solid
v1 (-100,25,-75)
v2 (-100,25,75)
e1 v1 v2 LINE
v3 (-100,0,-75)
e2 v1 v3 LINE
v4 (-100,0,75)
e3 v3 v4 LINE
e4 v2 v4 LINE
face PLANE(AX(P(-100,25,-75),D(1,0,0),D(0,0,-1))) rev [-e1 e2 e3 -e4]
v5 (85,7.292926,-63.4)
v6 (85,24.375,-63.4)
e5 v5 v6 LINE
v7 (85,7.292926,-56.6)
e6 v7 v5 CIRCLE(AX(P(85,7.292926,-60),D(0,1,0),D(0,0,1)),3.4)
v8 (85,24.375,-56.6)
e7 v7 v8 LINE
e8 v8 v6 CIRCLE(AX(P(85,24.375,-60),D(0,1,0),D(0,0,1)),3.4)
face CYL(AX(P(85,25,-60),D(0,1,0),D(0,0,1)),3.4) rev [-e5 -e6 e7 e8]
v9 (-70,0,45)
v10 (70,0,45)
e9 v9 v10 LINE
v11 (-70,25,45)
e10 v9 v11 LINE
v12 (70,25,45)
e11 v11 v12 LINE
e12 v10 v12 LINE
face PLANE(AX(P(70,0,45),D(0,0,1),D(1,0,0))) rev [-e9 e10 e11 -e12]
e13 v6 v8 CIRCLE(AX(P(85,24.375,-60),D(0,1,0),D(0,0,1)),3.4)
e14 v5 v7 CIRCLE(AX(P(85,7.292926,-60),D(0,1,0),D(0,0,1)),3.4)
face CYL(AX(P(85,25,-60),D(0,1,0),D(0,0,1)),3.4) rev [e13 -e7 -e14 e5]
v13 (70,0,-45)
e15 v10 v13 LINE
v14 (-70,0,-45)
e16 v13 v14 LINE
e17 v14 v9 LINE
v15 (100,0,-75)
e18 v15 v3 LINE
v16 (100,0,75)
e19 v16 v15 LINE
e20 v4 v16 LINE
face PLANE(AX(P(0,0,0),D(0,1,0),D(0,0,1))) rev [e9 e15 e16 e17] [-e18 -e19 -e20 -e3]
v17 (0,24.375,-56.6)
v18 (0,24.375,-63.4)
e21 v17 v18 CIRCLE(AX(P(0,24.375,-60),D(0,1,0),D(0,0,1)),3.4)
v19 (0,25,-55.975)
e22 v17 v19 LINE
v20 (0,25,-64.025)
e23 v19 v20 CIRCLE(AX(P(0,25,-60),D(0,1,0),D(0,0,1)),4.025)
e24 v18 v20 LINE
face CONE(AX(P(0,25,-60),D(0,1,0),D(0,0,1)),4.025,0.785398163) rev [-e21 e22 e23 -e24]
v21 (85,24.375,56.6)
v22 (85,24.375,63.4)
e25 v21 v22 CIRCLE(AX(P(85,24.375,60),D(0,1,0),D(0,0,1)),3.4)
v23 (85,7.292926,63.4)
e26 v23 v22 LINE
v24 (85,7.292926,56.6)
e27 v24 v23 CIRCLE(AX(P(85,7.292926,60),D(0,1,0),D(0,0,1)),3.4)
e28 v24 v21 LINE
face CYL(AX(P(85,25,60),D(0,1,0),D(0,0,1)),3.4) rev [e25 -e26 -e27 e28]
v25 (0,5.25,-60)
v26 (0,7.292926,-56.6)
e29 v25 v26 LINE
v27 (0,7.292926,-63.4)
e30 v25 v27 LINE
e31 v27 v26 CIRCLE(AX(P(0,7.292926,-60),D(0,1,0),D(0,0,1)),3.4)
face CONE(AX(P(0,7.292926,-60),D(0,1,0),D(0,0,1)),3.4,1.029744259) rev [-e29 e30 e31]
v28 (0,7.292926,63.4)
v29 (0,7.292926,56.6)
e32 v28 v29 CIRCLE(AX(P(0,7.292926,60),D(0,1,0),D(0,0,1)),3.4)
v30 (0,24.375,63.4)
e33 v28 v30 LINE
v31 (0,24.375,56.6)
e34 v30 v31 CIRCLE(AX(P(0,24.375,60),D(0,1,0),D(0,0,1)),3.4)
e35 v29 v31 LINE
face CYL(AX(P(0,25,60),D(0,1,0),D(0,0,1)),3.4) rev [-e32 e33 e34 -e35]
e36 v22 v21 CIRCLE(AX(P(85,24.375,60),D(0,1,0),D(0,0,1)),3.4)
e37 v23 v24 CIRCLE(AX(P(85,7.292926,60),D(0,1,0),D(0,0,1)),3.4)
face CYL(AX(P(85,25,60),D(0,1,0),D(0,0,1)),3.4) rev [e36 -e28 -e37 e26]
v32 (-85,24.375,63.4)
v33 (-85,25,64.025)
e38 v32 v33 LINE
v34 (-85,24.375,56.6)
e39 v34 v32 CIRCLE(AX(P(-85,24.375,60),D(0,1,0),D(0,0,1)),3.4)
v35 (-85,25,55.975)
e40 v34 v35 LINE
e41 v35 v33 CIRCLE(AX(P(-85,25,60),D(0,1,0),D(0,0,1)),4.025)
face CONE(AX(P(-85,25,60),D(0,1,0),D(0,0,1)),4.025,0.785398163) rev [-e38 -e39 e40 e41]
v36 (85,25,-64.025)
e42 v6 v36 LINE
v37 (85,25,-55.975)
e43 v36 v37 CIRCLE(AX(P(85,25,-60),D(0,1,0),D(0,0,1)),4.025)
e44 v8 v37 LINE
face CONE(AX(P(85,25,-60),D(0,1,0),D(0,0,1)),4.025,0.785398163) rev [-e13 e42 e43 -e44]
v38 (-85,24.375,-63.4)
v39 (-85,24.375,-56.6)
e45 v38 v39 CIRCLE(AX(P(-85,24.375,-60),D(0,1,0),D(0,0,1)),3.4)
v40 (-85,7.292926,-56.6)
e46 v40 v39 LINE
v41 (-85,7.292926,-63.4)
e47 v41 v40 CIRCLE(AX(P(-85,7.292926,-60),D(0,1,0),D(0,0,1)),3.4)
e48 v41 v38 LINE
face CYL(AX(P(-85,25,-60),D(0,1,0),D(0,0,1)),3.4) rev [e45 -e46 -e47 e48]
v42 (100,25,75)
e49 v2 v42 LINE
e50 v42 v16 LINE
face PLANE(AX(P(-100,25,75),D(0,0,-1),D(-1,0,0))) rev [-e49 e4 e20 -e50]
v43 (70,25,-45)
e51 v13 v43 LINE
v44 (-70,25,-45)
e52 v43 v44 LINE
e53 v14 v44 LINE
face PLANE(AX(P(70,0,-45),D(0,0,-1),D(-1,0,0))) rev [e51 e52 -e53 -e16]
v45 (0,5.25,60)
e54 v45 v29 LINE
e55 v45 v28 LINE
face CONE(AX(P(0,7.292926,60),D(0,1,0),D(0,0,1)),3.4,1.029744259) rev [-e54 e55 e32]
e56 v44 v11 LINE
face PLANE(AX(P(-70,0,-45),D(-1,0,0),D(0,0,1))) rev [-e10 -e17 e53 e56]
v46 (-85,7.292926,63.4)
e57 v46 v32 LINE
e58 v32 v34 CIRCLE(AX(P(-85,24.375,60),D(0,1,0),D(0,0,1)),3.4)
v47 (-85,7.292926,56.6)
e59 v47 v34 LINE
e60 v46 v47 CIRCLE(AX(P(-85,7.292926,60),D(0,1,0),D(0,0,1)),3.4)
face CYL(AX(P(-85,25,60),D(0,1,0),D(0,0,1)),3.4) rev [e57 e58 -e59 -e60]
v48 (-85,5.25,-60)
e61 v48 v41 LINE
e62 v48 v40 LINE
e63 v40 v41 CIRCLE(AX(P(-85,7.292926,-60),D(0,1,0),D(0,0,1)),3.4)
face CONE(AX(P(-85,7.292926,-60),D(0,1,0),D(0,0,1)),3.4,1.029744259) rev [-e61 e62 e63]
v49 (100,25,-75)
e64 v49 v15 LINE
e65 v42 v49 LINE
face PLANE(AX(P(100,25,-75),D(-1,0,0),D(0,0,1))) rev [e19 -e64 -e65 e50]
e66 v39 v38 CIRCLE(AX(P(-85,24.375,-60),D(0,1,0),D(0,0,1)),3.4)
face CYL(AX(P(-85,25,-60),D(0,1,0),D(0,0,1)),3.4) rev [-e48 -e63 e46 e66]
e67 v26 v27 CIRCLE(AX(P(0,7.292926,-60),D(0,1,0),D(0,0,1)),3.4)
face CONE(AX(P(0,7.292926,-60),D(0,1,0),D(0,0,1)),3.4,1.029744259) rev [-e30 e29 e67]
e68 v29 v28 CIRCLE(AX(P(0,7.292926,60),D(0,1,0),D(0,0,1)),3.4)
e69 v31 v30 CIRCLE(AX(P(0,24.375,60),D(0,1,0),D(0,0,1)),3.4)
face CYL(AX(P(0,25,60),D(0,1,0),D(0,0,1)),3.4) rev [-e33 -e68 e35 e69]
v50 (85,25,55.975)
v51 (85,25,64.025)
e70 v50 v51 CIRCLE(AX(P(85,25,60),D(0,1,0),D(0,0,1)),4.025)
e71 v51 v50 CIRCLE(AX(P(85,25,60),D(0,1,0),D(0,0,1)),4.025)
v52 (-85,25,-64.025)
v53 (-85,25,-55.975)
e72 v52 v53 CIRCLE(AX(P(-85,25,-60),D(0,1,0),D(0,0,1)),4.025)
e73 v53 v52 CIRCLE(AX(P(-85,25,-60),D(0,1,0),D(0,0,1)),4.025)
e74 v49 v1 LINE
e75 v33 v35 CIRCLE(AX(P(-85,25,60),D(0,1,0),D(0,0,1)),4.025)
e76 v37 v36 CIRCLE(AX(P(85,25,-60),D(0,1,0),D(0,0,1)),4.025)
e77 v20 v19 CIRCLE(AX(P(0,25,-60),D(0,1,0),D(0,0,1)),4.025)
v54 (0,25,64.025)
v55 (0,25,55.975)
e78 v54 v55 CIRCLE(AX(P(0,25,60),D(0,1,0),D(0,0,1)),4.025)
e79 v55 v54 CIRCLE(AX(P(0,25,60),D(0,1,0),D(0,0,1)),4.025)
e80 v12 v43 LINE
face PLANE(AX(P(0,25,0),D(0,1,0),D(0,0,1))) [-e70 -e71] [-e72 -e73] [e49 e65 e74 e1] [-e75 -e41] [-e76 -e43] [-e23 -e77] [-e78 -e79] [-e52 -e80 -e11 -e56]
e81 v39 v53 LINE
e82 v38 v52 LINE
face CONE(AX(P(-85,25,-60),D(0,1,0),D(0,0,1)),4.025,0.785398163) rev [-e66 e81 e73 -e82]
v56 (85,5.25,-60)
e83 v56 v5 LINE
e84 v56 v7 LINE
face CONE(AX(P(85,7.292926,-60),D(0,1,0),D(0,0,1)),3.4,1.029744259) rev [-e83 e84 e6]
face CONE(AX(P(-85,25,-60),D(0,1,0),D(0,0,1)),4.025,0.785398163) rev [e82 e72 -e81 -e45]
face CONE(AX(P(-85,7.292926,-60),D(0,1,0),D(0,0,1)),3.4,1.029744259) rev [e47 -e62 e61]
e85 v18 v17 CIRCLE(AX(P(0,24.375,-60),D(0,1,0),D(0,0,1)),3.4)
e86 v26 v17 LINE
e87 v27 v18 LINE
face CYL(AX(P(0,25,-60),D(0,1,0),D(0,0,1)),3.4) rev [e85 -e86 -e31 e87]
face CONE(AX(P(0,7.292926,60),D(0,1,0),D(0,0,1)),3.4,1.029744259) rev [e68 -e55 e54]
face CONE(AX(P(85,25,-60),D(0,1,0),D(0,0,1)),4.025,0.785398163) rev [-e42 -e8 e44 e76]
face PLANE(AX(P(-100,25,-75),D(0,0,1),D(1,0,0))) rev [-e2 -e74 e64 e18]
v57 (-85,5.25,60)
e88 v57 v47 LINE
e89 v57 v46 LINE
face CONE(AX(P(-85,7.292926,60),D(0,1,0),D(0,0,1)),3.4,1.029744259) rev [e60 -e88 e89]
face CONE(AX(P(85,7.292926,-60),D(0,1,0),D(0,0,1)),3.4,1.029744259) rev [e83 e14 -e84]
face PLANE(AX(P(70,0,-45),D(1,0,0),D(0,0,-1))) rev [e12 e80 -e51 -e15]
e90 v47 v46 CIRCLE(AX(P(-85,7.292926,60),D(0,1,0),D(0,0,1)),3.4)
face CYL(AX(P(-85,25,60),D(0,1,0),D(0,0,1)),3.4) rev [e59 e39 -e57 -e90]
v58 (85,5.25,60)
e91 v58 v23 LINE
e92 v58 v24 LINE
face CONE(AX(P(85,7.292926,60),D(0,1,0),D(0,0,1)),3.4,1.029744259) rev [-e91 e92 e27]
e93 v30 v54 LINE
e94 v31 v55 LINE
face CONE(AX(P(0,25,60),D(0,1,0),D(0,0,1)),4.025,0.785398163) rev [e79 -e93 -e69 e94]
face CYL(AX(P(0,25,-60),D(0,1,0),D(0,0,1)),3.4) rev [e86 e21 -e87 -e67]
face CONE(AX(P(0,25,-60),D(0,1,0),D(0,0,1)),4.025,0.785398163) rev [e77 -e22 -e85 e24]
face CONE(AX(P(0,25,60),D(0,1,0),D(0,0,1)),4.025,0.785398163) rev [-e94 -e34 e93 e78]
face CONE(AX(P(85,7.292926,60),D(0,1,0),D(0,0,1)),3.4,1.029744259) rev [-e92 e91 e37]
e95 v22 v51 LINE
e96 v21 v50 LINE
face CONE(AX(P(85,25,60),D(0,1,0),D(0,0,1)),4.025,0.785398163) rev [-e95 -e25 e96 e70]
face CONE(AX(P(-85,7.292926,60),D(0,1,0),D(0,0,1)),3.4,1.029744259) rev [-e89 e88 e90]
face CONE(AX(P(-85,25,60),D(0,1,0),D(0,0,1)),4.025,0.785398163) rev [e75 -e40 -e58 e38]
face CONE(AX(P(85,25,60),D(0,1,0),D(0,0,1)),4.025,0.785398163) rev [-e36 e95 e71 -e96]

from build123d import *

# Parameters (mm, degrees)
SKETCH_1_W                   = 200
SKETCH_1_H                   = 150
EXTRUDE_1_DEPTH              = 25
HOLE_WIZARD_M8_1_D           = 6.8
HOLE_WIZARD_M8_1_DEPTH       = 17.707073895
HOLE_WIZARD_M8_1_CSINK_D     = 8.05
HOLE_WIZARD_M8_1_CSINK_ANGLE = 90
HOLE_WIZARD_M8_1_TIP         = 2.042926105
CUT_EXTRUDE_1_DEPTH          = 128.47548784
CUT_EXTRUDE_1_DEPTH_BACK     = 128.47548784
SKETCH_5_W                   = 140
SKETCH_5_H                   = 90


with BuildPart() as part:
    # 草图1 → 凸台-拉伸1 (new body)
    with BuildSketch(Plane(origin=(0, 0, 0), x_dir=(1, 0, 0), z_dir=(0, 1, 0))):
        Rectangle(SKETCH_1_W, SKETCH_1_H)
    extrude(amount=EXTRUDE_1_DEPTH)

    # M8 螺纹孔1
    with Locations(Plane(origin=(0, 25, 0), x_dir=(1, 0, 0), z_dir=(0, 1, 0))):
        with Locations((-85, -60), (0, -60), (85, -60), (85, 60), (0, 60), (-85, 60)):
            CounterSinkHole(HOLE_WIZARD_M8_1_D / 2, HOLE_WIZARD_M8_1_CSINK_D / 2, depth=HOLE_WIZARD_M8_1_DEPTH, counter_sink_angle=HOLE_WIZARD_M8_1_CSINK_ANGLE)
            with Locations((0, 0, -(HOLE_WIZARD_M8_1_DEPTH + HOLE_WIZARD_M8_1_TIP / 2))):  # 118° drill point
                Cone(0, HOLE_WIZARD_M8_1_D / 2, HOLE_WIZARD_M8_1_TIP, mode=Mode.SUBTRACT)

    # 草图5 → 切除-拉伸1 (cut, two sides: drawn at the far end of the back side and taken through both)
    with BuildSketch(Plane(origin=(0, 25, 0), x_dir=(1, 0, 0), z_dir=(0, 1, 0)).offset(-CUT_EXTRUDE_1_DEPTH_BACK)):
        Rectangle(SKETCH_5_W, SKETCH_5_H)
    extrude(amount=CUT_EXTRUDE_1_DEPTH + CUT_EXTRUDE_1_DEPTH_BACK, mode=Mode.SUBTRACT)


solid = part.part
